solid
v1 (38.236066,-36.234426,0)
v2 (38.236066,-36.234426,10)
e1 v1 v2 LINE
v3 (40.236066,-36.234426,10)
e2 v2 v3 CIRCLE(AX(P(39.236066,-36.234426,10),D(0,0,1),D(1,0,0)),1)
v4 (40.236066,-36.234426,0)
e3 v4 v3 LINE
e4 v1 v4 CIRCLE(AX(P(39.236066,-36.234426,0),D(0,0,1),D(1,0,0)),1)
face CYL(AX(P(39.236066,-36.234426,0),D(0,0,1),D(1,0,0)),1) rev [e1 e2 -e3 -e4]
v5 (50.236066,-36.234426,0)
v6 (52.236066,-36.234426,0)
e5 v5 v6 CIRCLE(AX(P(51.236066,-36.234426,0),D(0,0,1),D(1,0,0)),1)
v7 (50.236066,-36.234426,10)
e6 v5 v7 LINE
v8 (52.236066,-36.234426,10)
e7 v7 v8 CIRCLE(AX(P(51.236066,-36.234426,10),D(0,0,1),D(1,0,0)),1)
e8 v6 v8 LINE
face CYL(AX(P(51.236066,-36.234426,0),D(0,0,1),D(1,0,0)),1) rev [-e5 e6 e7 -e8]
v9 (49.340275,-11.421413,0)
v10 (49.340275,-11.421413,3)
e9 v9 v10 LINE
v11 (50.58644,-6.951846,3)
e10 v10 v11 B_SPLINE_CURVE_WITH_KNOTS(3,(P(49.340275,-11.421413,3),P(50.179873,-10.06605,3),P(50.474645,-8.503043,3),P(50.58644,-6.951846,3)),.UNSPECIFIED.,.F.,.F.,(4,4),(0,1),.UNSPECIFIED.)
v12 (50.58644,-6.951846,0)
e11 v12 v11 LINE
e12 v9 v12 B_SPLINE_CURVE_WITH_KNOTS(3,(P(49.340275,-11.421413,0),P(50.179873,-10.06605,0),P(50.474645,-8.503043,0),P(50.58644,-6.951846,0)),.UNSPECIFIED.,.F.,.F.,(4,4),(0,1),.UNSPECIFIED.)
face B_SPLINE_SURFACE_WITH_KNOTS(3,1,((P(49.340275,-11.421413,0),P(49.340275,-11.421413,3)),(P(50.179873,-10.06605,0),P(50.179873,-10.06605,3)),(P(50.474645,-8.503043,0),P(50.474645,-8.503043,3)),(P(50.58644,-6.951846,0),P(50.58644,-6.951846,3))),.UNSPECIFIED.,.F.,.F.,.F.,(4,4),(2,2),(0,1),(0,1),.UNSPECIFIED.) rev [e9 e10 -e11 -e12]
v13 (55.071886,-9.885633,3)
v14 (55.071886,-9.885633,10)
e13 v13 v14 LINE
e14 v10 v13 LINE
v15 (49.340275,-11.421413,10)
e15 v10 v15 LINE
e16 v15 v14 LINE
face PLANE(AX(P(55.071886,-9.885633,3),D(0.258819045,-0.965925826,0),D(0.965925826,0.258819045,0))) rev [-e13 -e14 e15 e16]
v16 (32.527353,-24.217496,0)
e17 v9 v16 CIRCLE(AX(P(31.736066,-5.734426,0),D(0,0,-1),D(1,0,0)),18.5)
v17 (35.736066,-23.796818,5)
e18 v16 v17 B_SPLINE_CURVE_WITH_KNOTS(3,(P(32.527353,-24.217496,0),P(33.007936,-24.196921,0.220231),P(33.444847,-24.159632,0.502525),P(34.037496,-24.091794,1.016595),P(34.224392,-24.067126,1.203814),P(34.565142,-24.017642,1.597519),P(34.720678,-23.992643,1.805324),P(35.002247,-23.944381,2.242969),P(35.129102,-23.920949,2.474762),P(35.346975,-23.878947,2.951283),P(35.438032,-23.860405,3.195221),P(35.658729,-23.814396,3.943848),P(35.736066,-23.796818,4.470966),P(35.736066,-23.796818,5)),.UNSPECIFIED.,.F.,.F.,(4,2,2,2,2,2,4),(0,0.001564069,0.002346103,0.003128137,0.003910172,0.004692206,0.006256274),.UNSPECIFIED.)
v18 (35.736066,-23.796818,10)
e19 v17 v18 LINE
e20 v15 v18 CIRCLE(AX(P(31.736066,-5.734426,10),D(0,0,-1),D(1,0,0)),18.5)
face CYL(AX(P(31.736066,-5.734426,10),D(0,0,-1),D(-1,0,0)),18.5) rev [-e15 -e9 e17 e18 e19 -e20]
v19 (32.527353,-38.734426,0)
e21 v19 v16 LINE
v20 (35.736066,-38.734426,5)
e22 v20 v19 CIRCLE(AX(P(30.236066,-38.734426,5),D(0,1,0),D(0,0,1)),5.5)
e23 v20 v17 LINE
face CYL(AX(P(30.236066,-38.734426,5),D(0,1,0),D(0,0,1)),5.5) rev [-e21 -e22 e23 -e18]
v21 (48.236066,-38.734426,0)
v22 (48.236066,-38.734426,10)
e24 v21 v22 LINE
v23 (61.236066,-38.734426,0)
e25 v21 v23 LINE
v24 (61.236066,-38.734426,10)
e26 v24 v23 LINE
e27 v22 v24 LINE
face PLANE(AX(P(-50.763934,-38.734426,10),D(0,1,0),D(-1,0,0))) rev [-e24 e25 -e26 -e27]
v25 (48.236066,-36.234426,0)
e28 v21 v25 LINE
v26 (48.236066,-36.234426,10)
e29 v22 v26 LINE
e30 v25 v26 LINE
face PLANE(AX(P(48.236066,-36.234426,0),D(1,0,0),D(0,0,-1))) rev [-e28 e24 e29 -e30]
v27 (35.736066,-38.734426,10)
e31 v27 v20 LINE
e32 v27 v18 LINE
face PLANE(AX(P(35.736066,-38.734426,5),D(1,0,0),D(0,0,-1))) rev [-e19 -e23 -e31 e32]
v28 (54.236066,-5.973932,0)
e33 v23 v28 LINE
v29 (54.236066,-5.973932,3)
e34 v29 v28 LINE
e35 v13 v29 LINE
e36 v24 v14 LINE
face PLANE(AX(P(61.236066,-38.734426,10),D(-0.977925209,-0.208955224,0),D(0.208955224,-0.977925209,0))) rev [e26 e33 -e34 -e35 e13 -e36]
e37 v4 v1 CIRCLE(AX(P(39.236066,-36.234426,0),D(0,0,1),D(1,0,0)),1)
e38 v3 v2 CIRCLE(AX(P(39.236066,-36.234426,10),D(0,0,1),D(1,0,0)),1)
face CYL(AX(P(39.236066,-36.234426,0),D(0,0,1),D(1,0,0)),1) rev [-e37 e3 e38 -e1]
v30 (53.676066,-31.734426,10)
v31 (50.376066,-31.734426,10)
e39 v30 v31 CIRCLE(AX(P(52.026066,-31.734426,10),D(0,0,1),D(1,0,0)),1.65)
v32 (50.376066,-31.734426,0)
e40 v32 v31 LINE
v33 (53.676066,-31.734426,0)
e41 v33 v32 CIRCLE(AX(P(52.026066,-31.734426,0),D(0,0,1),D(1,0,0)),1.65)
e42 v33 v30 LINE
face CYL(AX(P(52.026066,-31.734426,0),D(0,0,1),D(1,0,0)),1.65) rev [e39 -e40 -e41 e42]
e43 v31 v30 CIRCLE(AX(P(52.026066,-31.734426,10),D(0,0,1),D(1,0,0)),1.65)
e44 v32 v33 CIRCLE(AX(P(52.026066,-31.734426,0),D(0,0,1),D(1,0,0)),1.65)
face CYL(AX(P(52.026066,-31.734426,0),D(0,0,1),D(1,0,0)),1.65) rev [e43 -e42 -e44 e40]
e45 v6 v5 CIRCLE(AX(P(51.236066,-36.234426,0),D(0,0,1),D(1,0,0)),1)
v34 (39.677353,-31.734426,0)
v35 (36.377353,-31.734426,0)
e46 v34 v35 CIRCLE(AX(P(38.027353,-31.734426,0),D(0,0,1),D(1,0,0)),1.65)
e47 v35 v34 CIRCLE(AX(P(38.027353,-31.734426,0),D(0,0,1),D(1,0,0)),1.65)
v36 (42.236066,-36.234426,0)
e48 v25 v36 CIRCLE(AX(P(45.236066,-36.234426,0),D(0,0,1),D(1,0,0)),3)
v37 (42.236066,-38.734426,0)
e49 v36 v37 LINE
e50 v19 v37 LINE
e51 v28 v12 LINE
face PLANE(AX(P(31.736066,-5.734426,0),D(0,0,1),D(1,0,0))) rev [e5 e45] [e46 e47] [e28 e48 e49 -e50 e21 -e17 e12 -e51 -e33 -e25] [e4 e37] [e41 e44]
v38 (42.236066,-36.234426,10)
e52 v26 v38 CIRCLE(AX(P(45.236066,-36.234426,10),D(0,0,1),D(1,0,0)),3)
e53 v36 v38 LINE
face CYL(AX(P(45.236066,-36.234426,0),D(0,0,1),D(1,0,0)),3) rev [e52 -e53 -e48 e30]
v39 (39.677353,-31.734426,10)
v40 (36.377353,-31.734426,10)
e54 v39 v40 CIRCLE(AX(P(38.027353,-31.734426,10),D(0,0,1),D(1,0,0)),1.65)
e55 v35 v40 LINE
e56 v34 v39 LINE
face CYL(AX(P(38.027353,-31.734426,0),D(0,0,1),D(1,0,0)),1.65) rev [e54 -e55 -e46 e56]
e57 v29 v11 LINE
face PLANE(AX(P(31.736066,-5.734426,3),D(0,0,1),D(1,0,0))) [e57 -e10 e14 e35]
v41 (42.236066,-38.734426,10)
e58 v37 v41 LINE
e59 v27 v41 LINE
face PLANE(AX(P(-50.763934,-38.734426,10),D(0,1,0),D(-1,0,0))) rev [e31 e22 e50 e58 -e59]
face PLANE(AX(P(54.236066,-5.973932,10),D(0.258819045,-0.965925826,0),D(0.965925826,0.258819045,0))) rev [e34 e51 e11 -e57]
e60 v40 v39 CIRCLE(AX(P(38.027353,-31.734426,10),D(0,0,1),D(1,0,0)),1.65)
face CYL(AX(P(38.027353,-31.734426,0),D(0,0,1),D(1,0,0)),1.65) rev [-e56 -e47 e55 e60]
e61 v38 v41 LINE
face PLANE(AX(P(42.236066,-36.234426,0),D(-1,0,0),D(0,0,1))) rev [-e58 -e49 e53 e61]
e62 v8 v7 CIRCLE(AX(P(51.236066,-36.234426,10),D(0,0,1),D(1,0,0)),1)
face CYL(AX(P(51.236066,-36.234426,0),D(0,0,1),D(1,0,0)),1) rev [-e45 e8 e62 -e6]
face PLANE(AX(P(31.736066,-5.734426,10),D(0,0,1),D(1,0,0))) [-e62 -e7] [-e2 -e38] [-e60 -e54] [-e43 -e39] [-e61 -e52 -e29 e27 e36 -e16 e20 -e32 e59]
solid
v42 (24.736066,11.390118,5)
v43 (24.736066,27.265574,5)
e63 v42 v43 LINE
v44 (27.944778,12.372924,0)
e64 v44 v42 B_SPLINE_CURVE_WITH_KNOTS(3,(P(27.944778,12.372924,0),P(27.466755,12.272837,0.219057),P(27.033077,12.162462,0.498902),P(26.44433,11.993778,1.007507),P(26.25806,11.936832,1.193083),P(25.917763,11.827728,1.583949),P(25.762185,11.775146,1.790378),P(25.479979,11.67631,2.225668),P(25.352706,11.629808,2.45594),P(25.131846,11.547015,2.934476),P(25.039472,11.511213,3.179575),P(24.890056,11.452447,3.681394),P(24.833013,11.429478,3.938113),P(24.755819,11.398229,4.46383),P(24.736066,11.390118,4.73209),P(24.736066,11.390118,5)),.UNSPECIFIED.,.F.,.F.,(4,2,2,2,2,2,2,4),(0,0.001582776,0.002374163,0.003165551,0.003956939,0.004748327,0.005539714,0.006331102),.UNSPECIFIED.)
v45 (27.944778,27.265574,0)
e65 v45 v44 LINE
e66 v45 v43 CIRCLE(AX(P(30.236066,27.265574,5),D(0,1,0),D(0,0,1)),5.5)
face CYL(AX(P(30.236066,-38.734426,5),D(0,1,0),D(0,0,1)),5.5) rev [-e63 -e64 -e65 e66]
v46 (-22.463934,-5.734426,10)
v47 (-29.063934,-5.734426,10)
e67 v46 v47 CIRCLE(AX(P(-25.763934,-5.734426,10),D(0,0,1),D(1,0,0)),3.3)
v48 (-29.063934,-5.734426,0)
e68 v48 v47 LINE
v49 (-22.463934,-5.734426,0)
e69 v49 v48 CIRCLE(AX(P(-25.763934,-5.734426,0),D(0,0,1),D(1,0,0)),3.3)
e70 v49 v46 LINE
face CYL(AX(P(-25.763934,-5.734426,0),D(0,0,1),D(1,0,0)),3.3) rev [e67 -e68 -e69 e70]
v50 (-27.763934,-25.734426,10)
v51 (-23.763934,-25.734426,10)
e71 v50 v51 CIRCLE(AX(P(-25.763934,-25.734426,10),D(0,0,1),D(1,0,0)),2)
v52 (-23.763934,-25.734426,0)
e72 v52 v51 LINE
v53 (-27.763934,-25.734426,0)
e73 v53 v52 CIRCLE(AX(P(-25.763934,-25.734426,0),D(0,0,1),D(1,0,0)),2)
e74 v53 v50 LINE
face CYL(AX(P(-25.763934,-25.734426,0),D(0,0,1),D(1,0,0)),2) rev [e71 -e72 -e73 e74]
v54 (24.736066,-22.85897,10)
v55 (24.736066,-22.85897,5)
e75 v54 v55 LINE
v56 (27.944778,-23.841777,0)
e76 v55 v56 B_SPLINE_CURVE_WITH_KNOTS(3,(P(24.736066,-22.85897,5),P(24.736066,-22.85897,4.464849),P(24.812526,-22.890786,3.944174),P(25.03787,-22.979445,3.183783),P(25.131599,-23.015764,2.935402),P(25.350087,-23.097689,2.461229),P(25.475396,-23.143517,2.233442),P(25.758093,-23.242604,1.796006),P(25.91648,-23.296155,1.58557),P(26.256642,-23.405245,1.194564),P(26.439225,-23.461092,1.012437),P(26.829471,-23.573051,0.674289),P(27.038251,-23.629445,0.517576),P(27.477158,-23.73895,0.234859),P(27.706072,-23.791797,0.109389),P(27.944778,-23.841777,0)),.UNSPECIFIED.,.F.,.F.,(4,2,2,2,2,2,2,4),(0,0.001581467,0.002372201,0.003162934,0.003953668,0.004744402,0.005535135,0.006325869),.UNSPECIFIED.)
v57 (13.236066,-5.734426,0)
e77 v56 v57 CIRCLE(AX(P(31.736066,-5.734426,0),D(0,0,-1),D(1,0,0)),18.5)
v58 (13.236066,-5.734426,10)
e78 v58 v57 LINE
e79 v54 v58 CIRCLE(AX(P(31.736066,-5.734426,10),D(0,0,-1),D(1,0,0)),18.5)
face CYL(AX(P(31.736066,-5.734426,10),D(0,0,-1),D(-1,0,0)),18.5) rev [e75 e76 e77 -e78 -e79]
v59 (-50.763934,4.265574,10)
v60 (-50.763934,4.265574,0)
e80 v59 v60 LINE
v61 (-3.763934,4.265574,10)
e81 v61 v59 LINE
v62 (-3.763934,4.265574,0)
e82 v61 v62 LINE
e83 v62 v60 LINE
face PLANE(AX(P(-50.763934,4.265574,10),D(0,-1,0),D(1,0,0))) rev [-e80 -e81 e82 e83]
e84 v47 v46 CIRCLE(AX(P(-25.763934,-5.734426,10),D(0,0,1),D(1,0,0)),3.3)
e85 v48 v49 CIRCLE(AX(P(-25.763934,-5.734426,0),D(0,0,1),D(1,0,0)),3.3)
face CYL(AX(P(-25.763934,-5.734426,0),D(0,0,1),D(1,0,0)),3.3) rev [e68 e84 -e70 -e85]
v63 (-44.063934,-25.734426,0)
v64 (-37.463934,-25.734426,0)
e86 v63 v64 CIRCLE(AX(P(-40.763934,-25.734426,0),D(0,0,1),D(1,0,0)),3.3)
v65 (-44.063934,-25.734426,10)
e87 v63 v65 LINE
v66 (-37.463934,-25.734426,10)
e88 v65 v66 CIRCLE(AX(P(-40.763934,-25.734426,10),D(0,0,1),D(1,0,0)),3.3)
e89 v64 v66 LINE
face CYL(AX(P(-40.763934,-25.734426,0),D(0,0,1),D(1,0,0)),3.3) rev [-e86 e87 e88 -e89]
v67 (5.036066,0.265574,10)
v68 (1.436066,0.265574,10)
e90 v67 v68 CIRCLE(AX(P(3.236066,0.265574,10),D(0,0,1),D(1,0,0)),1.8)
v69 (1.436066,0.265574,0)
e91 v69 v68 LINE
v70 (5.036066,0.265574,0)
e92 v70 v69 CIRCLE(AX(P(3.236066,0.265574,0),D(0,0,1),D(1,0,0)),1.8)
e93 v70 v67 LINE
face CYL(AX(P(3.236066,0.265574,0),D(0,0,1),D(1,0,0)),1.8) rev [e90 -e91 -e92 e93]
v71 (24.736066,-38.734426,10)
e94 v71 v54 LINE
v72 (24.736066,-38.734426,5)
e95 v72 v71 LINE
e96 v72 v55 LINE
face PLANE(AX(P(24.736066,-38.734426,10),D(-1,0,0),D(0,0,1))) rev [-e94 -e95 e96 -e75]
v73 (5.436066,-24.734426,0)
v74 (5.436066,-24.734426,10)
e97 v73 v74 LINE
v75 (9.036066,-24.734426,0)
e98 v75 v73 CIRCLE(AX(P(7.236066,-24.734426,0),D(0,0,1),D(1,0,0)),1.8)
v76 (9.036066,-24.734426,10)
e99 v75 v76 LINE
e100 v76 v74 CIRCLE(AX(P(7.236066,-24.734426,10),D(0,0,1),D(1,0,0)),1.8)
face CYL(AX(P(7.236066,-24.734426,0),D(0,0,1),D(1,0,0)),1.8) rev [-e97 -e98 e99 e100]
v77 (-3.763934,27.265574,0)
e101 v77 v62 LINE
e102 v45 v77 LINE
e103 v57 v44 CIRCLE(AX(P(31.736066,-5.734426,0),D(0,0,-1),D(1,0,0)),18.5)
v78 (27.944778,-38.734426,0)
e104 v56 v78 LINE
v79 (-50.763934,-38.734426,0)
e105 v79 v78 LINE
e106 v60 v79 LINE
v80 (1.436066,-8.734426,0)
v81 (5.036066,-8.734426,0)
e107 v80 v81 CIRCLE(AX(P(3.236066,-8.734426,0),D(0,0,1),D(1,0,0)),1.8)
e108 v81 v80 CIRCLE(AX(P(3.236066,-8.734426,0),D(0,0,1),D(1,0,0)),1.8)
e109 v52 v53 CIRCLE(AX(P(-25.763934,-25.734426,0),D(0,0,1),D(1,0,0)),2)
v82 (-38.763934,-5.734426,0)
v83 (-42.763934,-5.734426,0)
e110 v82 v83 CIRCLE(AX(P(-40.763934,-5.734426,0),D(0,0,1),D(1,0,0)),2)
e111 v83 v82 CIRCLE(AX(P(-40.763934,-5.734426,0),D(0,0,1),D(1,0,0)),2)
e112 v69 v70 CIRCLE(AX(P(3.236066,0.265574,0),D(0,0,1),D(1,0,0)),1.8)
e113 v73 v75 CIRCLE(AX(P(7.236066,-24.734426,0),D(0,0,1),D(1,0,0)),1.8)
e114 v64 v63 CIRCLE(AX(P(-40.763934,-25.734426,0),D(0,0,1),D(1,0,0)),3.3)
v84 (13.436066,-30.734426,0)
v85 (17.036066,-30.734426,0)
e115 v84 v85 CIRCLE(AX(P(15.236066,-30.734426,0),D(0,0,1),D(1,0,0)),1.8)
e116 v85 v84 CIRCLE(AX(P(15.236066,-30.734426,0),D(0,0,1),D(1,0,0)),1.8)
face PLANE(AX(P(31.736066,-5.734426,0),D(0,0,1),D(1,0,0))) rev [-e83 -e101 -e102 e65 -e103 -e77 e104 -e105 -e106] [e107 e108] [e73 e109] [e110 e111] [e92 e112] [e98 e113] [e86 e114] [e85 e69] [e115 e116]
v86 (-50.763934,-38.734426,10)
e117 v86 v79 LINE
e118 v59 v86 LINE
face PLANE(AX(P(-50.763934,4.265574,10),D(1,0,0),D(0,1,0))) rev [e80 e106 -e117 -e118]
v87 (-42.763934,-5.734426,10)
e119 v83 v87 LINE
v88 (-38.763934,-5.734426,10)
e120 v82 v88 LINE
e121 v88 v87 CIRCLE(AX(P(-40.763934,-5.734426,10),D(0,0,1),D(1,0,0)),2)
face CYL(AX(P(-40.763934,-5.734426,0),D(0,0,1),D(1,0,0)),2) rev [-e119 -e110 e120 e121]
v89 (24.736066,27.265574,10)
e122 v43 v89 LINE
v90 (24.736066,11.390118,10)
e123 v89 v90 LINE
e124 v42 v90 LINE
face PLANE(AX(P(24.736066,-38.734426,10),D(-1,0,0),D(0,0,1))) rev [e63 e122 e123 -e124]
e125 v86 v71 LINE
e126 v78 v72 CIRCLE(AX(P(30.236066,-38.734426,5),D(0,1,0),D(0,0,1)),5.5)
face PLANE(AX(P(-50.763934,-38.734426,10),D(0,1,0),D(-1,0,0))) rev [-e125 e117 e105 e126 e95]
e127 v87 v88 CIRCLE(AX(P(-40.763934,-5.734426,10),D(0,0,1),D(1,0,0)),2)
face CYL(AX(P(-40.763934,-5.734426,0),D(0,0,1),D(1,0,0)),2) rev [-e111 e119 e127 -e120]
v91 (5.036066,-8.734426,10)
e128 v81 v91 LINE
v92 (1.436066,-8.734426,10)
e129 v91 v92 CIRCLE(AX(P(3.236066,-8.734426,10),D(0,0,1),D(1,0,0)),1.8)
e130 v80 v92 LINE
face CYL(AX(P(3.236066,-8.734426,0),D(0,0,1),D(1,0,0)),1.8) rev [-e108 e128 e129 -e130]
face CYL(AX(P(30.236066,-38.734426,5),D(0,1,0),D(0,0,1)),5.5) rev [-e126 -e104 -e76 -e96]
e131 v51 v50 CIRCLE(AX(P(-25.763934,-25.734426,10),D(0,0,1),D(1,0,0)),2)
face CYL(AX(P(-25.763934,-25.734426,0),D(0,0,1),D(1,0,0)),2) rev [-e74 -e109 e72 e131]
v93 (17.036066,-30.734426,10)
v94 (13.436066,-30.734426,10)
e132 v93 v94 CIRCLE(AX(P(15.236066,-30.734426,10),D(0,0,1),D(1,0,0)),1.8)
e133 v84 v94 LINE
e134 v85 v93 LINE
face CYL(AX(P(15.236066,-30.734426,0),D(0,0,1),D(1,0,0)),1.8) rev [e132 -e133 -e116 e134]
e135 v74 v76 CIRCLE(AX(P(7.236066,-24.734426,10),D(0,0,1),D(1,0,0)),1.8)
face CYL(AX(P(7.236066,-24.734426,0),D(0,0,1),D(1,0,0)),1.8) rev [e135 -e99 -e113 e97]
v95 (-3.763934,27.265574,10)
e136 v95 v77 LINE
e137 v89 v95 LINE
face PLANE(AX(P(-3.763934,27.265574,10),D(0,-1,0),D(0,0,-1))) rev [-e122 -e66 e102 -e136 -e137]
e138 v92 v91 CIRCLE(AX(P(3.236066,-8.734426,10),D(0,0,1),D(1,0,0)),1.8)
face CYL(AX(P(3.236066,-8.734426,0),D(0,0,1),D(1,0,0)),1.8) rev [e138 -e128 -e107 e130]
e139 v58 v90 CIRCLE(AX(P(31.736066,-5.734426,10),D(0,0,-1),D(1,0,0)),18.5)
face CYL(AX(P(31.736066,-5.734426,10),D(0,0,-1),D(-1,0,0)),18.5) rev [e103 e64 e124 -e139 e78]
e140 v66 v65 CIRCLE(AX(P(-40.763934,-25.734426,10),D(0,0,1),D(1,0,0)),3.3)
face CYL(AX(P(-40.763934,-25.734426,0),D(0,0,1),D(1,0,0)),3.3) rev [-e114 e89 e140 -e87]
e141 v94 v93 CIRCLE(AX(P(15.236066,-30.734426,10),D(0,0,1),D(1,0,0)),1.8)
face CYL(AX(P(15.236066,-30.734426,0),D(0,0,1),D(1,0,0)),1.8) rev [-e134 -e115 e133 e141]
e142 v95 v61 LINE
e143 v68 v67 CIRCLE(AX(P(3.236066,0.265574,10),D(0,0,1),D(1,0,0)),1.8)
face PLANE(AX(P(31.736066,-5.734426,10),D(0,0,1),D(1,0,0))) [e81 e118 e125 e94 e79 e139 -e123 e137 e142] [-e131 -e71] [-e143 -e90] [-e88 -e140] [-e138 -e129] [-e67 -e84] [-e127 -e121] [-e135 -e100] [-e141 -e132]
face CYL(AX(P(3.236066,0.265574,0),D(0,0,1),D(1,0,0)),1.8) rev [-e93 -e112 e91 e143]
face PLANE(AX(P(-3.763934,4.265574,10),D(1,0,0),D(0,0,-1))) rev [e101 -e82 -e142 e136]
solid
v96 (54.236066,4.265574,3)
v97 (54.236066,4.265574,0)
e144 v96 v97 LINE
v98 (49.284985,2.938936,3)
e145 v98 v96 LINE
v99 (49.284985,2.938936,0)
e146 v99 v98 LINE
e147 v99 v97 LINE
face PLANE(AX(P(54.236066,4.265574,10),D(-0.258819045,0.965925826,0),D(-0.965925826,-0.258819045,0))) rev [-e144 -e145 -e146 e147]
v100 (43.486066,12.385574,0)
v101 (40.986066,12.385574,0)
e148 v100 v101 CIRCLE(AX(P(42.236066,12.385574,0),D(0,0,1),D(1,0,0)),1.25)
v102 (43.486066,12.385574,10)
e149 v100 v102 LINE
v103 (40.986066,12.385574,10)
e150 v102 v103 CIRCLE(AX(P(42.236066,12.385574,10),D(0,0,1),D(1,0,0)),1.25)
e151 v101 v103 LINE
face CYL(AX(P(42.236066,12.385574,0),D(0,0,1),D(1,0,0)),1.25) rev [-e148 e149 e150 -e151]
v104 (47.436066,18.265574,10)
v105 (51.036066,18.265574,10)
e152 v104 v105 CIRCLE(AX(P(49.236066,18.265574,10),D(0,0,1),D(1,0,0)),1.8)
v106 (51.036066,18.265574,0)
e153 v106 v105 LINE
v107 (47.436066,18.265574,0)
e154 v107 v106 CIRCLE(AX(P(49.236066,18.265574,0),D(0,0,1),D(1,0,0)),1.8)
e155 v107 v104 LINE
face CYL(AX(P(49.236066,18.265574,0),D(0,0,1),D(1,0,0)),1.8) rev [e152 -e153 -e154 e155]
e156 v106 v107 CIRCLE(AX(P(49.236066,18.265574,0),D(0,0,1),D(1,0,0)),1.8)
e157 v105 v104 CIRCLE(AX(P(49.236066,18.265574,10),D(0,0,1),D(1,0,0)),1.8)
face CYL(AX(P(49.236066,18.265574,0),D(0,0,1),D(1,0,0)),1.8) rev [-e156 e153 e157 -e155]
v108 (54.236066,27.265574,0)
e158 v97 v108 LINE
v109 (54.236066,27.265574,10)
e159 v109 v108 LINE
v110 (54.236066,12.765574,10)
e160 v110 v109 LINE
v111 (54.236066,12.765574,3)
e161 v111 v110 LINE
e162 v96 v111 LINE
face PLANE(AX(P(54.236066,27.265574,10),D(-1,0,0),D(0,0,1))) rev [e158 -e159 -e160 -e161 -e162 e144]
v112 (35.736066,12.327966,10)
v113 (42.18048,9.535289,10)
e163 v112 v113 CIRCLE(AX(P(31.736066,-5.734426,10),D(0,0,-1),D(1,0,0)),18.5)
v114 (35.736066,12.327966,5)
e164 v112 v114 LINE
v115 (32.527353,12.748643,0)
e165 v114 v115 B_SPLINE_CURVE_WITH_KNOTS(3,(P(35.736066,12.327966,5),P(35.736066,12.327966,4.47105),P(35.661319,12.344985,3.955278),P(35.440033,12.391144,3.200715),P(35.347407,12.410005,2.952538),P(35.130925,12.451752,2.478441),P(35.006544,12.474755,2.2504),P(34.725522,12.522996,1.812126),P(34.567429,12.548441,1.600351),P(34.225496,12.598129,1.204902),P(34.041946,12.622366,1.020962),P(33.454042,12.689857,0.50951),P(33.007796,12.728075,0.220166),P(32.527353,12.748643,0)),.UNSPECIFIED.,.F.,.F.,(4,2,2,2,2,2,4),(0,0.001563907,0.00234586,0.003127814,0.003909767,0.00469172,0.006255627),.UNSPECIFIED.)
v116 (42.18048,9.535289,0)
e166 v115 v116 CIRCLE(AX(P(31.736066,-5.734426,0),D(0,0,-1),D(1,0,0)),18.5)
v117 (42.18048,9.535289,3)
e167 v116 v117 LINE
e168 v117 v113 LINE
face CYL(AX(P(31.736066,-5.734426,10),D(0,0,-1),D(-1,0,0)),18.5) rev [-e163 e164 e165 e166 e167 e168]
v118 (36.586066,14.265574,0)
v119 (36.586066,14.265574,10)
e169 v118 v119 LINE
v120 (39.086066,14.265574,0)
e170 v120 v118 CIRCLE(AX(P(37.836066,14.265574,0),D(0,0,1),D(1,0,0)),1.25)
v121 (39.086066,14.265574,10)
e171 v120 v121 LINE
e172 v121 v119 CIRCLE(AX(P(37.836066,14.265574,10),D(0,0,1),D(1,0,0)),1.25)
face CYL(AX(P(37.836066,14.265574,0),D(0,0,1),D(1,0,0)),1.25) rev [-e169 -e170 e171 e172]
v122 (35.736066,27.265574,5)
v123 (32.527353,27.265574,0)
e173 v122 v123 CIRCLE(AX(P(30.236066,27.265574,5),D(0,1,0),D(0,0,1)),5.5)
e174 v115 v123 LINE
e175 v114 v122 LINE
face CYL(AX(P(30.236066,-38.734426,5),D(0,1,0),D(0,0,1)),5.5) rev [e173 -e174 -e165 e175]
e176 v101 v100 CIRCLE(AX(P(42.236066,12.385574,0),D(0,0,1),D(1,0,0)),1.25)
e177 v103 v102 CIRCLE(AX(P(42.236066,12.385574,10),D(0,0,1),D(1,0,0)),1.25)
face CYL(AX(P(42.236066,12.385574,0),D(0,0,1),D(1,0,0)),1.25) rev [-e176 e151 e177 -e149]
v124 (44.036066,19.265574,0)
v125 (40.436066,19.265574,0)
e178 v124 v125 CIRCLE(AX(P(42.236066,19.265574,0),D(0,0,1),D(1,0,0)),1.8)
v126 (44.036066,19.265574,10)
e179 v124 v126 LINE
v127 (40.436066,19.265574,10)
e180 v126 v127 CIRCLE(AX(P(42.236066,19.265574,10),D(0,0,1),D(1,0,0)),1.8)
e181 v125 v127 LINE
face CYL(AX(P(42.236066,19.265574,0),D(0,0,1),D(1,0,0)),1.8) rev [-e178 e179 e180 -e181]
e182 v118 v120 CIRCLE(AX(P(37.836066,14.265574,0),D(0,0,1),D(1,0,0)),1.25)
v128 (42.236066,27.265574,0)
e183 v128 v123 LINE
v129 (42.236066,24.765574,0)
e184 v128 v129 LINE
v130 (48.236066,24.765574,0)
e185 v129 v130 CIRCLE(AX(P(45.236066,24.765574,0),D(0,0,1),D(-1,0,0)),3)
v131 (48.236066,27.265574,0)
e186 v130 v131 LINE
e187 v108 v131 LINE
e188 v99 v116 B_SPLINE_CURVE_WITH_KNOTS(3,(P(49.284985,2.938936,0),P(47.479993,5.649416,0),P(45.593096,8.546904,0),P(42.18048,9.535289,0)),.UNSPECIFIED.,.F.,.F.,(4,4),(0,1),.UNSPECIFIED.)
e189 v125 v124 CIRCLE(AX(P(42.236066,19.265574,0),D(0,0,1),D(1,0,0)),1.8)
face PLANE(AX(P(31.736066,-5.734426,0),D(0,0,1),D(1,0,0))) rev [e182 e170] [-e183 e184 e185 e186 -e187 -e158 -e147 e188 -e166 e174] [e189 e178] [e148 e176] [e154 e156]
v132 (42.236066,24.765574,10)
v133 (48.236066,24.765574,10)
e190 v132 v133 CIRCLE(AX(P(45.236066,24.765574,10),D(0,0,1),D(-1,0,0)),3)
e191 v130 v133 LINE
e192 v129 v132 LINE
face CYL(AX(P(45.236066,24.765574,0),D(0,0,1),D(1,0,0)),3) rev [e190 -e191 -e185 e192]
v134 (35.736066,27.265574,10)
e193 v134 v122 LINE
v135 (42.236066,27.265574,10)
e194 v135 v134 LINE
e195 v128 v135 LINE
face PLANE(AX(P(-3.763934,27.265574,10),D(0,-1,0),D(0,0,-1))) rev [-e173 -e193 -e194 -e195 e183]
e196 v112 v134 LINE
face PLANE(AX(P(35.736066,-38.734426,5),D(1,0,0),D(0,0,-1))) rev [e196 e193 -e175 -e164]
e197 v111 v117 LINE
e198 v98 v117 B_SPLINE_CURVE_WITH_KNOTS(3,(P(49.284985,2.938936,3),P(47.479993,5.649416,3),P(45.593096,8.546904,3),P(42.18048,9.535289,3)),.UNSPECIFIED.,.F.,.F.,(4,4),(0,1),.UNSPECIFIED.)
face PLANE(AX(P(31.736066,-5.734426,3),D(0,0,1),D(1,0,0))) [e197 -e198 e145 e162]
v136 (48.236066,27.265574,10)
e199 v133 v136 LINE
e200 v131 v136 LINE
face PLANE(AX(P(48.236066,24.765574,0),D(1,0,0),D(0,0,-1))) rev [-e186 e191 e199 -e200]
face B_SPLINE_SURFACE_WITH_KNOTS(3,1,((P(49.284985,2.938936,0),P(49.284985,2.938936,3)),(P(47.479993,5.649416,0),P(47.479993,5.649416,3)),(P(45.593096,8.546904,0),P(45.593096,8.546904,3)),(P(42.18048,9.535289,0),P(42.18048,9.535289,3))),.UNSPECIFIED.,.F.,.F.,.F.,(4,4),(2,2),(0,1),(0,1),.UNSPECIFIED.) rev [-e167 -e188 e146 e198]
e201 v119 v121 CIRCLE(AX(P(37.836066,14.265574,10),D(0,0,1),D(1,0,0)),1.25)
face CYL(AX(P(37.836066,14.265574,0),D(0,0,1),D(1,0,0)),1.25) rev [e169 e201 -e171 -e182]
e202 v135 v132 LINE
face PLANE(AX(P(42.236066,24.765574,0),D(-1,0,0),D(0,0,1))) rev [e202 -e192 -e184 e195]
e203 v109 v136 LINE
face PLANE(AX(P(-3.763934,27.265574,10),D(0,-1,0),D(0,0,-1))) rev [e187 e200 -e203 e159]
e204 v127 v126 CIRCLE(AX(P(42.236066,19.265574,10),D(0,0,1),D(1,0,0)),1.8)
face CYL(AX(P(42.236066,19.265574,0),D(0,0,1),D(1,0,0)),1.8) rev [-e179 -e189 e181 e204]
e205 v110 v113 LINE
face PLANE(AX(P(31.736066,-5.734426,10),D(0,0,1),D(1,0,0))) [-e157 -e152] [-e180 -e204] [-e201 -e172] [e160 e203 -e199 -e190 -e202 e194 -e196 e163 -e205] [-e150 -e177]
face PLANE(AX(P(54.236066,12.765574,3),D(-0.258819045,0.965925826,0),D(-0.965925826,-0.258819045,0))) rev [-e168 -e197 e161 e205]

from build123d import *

# Parameters (mm, degrees)
EXTRUDE_1_DEPTH     = 10
CUT_EXTRUDE_1_DEPTH = 91.586178454
CUT_EXTRUDE_2_DEPTH = 7
CUT_EXTRUDE_3_DEPTH = 74.145140044
SKETCH_5_R          = 2
SKETCH_5_R_2        = 3.3
SKETCH_5_R_3        = 1.8
SKETCH_5_R_4        = 1.65
SKETCH_5_R_5        = 1.25
SKETCH_5_R_6        = 1
CUT_EXTRUDE_4_DEPTH = 74.145140044
CUT_EXTRUDE_5_DEPTH = 10
CUT_EXTRUDE_6_DEPTH = 10


with BuildPart() as part:
    # 草图1 → 凸台-拉伸1 (new body)
    with BuildSketch(Plane.XY):
        with BuildLine():
            Line((-50.763934426, 4.26557377), (-3.763934426, 4.26557377))
            Line((-3.763934426, 4.26557377), (-3.763934426, 27.26557377))
            Line((-3.763934426, 27.26557377), (54.236065574, 27.26557377))
            Line((54.236065574, 27.26557377), (54.236065574, 4.26557377))
            Line((54.236065574, 4.26557377), (48.224573526, 2.654799331))
            ThreePointArc((48.224573526, 2.654799331), (13.603048186, -9.400988707), (50.188626042, -7.058439882))
            Line((50.188626042, -7.058439882), (54.236065574, -5.973931728))
            Line((54.236065574, -5.973931728), (61.236065574, -38.73442623))
            Line((61.236065574, -38.73442623), (-50.763934426, -38.73442623))
            Line((-50.763934426, -38.73442623), (-50.763934426, 4.26557377))
        make_face()
    extrude(amount=EXTRUDE_1_DEPTH)

    # 草图2 → 切除-拉伸1 (cut, through all)
    with BuildSketch(Plane(origin=(0, 27.26557377, 0), x_dir=(1, 0, 0), z_dir=(0, 1, 0))):
        with BuildLine():
            Line((35.736065574, -5), (35.736065574, -10))
            Line((35.736065574, -10), (24.736065574, -10))
            Line((24.736065574, -10), (24.736065574, -5))
            ThreePointArc((24.736065574, -5), (30.236065574, 0.5), (35.736065574, -5))
        make_face()
    extrude(amount=-CUT_EXTRUDE_1_DEPTH, mode=Mode.SUBTRACT)


with BuildPart() as cut_extrude_1_piece_1:
    # of the separate pieces the step leaves, piece 1, a body of its own (cut_extrude_1_pieces)
    add(part.part.solids().sort_by_distance((-50.763934426, 4.26557377, 0))[0])


with BuildPart() as cut_extrude_1_piece_2:
    # of the separate pieces the step leaves, piece 2, a body of its own (cut_extrude_1_pieces)
    add(part.part.solids().sort_by_distance((61.236065574, -38.73442623, 0))[0])


with BuildPart() as cut_extrude_1_piece_3:
    # of the separate pieces the step leaves, piece 3, a body of its own (cut_extrude_1_pieces)
    add(part.part.solids().sort_by_distance((32.527353421, 12.748643417, 0))[0])


with BuildPart() as cut_extrude_2_tool:
    # 草图3 → 切除-拉伸2 (new body)
    with BuildSketch(Plane.XY.offset(10)):
        with BuildLine():
            Line((54.236065574, 4.26557377), (54.236065574, 12.76557377))
            Line((54.236065574, 12.76557377), (42.180479772, 9.535289291))
            ThreePointArc((42.180479772, 9.535289291), (45.635017312, 6.474961167), (48.224573526, 2.654799331))
            Line((48.224573526, 2.654799331), (54.236065574, 4.26557377))
        make_face()
        with BuildLine():
            Line((54.236065574, -5.973931728), (55.071886469, -9.885632564))
            Line((55.071886469, -9.885632564), (49.340274669, -11.421413317))
            ThreePointArc((49.340274669, -11.421413317), (49.895953848, -9.265496585), (50.188626042, -7.058439882))
            Line((50.188626042, -7.058439882), (54.236065574, -5.973931728))
        make_face()
    extrude(amount=-CUT_EXTRUDE_2_DEPTH)


with BuildPart() as cut_extrude_1_piece_2_1:
    add(cut_extrude_1_piece_2.part)

    # 切除-拉伸2: cut by cut_extrude_2_tool
    add(cut_extrude_2_tool.part, mode=Mode.SUBTRACT)


with BuildPart() as cut_extrude_1_piece_3_1:
    add(cut_extrude_1_piece_3.part)

    # 切除-拉伸2: cut by cut_extrude_2_tool
    add(cut_extrude_2_tool.part, mode=Mode.SUBTRACT)


with BuildPart() as cut_extrude_3_tool:
    # 草图4 → 切除-拉伸3 (new, through all)
    with BuildSketch(Plane.XY.offset(10)):
        with BuildLine():
            Line((42.236065574, -36.23442623), (42.236065574, -38.73442623))
            Line((42.236065574, -38.73442623), (48.236065574, -38.73442623))
            Line((48.236065574, -38.73442623), (48.236065574, -36.23442623))
            ThreePointArc((48.236065574, -36.23442623), (45.236065574, -33.23442623), (42.236065574, -36.23442623))
        make_face()
        with BuildLine():
            Line((48.236065574, 27.26557377), (42.236065574, 27.26557377))
            Line((42.236065574, 27.26557377), (42.236065574, 24.76557377))
            ThreePointArc((42.236065574, 24.76557377), (45.236065574, 21.76557377), (48.236065574, 24.76557377))
            Line((48.236065574, 24.76557377), (48.236065574, 27.26557377))
        make_face()
    extrude(amount=-CUT_EXTRUDE_3_DEPTH)


with BuildPart() as cut_extrude_1_piece_2_2:
    add(cut_extrude_1_piece_2_1.part)

    # 切除-拉伸3: cut by cut_extrude_3_tool
    add(cut_extrude_3_tool.part, mode=Mode.SUBTRACT)


with BuildPart() as cut_extrude_1_piece_3_2:
    add(cut_extrude_1_piece_3_1.part)

    # 切除-拉伸3: cut by cut_extrude_3_tool
    add(cut_extrude_3_tool.part, mode=Mode.SUBTRACT)


with BuildPart() as cut_extrude_4_tool:
    # 草图5 → 切除-拉伸4 (new, through all)
    with BuildSketch(Plane.XY.offset(10)):
        with Locations((-40.763934426, -5.73442623)):
            Circle(SKETCH_5_R)
        with Locations((-40.763934426, -25.73442623)):
            Circle(SKETCH_5_R_2)
        with Locations((-25.763934426, -5.73442623)):
            Circle(SKETCH_5_R_2)
        with Locations((-25.763934426, -25.73442623)):
            Circle(SKETCH_5_R)
        with Locations((7.236065574, -24.73442623)):
            Circle(SKETCH_5_R_3)
        with Locations((15.236065574, -30.73442623)):
            Circle(SKETCH_5_R_3)
        with Locations((3.236065574, 0.26557377)):
            Circle(SKETCH_5_R_3)
        with Locations((3.236065574, -8.73442623)):
            Circle(SKETCH_5_R_3)
        with Locations((38.027353421, -31.73442623)):
            Circle(SKETCH_5_R_4)
        with Locations((52.026065574, -31.73442623)):
            Circle(SKETCH_5_R_4)
        with Locations((42.236065574, 19.26557377)):
            Circle(SKETCH_5_R_3)
        with Locations((49.236065574, 18.26557377)):
            Circle(SKETCH_5_R_3)
        with Locations((37.836065574, 14.26557377)):
            Circle(SKETCH_5_R_5)
        with Locations((42.236065574, 12.38557377)):
            Circle(SKETCH_5_R_5)
        with Locations((39.236065574, -36.23442623)):
            Circle(SKETCH_5_R_6)
        with Locations((51.236065574, -36.23442623)):
            Circle(SKETCH_5_R_6)
    extrude(amount=-CUT_EXTRUDE_4_DEPTH)


with BuildPart() as cut_extrude_1_piece_1_1:
    add(cut_extrude_1_piece_1.part)

    # 切除-拉伸4: cut by cut_extrude_4_tool
    add(cut_extrude_4_tool.part, mode=Mode.SUBTRACT)


with BuildPart() as cut_extrude_1_piece_2_3:
    add(cut_extrude_1_piece_2_2.part)

    # 切除-拉伸4: cut by cut_extrude_4_tool
    add(cut_extrude_4_tool.part, mode=Mode.SUBTRACT)

    # 草图7 → 切除-拉伸6 (cut)
    with BuildSketch(Plane.XY.offset(3)):
        with BuildLine():
            Line((50.586440047, -6.95184594), (50.188626042, -7.058439882))
            ThreePointArc((50.188626042, -7.058439882), (49.895953848, -9.265496585), (49.340274669, -11.421413317))
            add(Edge.make_bspline(
                [(49.340274669, -11.421413317), (50.179872923, -10.066049912), (50.47464498, -8.503042836), (50.586440047, -6.95184594)],
                knots=[0, 0, 0, 0, 1, 1, 1, 1], degree=3))
        make_face()
    extrude(amount=-CUT_EXTRUDE_6_DEPTH, mode=Mode.SUBTRACT)


with BuildPart() as cut_extrude_1_piece_3_3:
    add(cut_extrude_1_piece_3_2.part)

    # 切除-拉伸4: cut by cut_extrude_4_tool
    add(cut_extrude_4_tool.part, mode=Mode.SUBTRACT)

    # 草图6 → 切除-拉伸5 (cut)
    with BuildSketch(Plane.XY.offset(3)):
        with BuildLine():
            Line((49.284985205, 2.938935784), (48.224573526, 2.654799331))
            ThreePointArc((48.224573526, 2.654799331), (45.635017312, 6.474961167), (42.180479772, 9.535289291))
            add(Edge.make_bspline(
                [(42.180479772, 9.535289291), (45.593095673, 8.546903827), (47.47999295, 5.649415813), (49.284985205, 2.938935784)],
                knots=[0, 0, 0, 0, 1, 1, 1, 1], degree=3))
        make_face()
    extrude(amount=-CUT_EXTRUDE_5_DEPTH, mode=Mode.SUBTRACT)


solid = Compound([cut_extrude_1_piece_1_1.part, cut_extrude_1_piece_2_3.part, cut_extrude_1_piece_3_3.part])
